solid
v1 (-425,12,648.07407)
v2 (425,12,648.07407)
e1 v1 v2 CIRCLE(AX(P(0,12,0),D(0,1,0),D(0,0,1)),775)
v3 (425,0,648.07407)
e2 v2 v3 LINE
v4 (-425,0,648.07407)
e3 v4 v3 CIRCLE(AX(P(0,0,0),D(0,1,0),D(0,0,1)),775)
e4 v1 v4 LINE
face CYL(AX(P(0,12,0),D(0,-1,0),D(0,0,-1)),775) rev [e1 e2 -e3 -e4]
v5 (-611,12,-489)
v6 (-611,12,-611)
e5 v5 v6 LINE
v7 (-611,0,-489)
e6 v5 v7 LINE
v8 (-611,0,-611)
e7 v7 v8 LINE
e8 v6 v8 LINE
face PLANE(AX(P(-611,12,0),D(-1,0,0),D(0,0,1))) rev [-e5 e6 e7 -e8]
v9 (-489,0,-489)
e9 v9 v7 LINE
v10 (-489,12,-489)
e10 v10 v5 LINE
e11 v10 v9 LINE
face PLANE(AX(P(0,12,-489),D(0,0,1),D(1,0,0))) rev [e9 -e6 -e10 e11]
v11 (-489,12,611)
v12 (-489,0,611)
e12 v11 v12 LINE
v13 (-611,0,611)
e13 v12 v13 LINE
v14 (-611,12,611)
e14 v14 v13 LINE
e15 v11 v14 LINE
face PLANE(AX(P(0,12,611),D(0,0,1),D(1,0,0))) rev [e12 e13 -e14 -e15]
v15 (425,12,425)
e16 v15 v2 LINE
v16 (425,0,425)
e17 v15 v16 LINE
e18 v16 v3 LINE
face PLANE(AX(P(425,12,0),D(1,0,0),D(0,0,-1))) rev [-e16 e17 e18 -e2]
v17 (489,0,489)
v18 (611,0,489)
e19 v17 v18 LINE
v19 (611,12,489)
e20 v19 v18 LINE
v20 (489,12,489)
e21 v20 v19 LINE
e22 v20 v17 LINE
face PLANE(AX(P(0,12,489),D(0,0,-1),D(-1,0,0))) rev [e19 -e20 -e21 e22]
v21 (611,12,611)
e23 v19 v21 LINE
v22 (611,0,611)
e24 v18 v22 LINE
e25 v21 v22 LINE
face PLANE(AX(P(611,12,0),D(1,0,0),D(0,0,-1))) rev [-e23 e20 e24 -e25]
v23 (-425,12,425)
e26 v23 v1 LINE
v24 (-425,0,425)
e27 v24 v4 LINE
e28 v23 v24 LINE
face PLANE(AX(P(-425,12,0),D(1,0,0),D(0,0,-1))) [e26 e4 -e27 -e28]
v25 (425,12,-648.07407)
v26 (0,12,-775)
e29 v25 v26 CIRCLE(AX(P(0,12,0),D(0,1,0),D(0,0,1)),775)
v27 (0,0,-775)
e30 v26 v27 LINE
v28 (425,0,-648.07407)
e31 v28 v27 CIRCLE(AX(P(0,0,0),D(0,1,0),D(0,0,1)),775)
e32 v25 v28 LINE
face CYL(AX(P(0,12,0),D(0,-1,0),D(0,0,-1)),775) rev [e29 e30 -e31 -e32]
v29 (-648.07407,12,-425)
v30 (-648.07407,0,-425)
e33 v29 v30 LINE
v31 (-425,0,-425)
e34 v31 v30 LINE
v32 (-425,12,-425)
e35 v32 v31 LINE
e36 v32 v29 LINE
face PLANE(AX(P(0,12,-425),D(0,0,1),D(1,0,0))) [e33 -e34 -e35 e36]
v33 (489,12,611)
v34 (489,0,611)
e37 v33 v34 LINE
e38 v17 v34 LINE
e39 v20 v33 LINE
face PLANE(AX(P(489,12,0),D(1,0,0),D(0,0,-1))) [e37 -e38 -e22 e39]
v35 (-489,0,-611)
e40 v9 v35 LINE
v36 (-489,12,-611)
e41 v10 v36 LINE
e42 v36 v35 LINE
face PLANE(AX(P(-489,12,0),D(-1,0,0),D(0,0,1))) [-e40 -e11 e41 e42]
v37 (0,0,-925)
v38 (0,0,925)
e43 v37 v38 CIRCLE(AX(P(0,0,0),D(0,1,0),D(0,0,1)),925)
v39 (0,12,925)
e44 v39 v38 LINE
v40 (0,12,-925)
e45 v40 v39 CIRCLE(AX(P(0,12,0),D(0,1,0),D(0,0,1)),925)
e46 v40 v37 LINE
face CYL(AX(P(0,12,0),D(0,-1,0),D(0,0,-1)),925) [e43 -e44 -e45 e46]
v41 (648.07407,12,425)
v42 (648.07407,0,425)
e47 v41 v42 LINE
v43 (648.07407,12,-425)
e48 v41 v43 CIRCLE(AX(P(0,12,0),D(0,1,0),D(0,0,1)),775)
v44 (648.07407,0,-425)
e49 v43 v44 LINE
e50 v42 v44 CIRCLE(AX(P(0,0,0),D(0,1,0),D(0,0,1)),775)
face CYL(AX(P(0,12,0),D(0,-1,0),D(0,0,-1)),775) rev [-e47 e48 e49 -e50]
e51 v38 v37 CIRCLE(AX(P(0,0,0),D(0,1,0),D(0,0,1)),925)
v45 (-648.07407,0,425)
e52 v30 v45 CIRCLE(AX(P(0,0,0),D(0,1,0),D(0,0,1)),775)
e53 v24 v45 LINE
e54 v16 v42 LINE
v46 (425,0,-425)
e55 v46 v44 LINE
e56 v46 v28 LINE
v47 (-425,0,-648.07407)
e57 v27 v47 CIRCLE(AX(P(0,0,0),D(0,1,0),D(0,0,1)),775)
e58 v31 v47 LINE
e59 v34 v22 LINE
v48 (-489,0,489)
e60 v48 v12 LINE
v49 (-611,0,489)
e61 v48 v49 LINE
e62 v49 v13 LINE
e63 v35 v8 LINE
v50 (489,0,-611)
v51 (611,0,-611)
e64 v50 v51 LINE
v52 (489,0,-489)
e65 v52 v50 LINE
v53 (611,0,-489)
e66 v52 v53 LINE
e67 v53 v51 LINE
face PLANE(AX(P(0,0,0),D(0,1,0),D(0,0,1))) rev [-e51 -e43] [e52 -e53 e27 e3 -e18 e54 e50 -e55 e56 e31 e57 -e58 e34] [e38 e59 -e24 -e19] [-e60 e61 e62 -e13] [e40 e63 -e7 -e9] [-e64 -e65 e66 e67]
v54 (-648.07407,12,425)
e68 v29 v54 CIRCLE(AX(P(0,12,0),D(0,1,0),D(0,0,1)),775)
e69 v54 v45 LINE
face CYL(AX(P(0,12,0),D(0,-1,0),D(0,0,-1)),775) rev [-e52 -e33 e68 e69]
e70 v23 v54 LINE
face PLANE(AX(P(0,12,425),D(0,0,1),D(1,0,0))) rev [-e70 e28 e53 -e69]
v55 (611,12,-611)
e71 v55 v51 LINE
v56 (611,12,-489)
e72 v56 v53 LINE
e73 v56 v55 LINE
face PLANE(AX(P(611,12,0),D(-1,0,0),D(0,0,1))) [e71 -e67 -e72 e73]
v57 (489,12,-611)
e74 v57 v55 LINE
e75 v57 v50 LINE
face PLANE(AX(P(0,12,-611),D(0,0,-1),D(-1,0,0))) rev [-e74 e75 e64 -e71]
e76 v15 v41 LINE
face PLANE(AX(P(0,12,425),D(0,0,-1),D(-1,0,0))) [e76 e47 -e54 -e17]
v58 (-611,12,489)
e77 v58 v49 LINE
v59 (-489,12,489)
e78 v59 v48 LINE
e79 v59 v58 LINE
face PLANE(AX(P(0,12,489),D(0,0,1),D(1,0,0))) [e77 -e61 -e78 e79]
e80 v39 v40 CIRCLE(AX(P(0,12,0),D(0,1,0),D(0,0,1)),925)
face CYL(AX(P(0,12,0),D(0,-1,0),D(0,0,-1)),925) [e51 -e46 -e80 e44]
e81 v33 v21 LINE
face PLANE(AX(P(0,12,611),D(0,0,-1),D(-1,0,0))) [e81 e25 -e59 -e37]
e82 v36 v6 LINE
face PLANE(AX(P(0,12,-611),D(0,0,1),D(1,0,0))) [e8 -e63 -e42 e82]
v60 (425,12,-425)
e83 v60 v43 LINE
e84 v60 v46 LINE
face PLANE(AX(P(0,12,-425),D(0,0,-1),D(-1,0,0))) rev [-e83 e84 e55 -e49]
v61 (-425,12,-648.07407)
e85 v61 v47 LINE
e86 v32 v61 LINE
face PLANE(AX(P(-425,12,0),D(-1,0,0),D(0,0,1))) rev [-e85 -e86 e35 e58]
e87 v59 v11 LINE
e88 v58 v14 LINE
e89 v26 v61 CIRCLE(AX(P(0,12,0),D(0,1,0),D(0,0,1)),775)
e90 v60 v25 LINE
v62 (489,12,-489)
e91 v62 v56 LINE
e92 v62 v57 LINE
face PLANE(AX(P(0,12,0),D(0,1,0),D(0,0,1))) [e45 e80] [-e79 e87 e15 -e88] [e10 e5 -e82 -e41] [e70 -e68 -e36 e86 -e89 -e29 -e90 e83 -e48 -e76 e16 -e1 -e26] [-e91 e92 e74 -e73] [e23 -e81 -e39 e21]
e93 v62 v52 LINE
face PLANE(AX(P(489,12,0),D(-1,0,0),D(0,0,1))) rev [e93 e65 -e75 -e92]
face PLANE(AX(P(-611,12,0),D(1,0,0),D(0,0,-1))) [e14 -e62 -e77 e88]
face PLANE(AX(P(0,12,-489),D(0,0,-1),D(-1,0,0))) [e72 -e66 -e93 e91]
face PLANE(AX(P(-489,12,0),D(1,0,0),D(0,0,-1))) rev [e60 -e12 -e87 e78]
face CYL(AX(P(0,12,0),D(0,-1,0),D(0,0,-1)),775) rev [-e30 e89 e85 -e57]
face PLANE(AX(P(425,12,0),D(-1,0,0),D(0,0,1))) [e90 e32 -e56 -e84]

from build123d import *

# Parameters (mm, degrees)
SKETCH_1_R      = 925
SKETCH_1_W      = 122
SKETCH_1_H      = 122
EXTRUDE_1_DEPTH = 12


with BuildPart() as part:
    # 草图1 → 凸台-拉伸1 (new body)
    with BuildSketch(Plane(origin=(0, 0, 0), x_dir=(1, 0, 0), z_dir=(0, 1, 0))):
        with Locations(Location((0, 0, 0), (0, 0, 270))):
            Circle(SKETCH_1_R)
        with BuildLine():
            Line((-648.074069841, 425), (-425, 425))
            Line((-425, 425), (-425, 648.074069841))
            ThreePointArc((-425, 648.074069841), (0, 775), (425, 648.074069841))
            Line((425, 648.074069841), (425, 425))
            Line((425, 425), (648.074069841, 425))
            ThreePointArc((648.074069841, 425), (775, 0), (648.074069841, -425))
            Line((648.074069841, -425), (425, -425))
            Line((425, -425), (425, -648.074069841))
            ThreePointArc((425, -648.074069841), (0, -775), (-425, -648.074069841))
            Line((-425, -648.074069841), (-425, -425))
            Line((-425, -425), (-648.074069841, -425))
            ThreePointArc((-648.074069841, -425), (-775, 0), (-648.074069841, 425))
        make_face(mode=Mode.SUBTRACT)
        with Locations((-550, 550)):
            Rectangle(SKETCH_1_W, SKETCH_1_H, mode=Mode.SUBTRACT)
        with Locations((-550, -550)):
            Rectangle(SKETCH_1_W, SKETCH_1_H, mode=Mode.SUBTRACT)
        with Locations((550, -550)):
            Rectangle(SKETCH_1_W, SKETCH_1_H, mode=Mode.SUBTRACT)
        with Locations((550, 550)):
            Rectangle(SKETCH_1_W, SKETCH_1_H, mode=Mode.SUBTRACT)
    extrude(amount=EXTRUDE_1_DEPTH)


solid = part.part
